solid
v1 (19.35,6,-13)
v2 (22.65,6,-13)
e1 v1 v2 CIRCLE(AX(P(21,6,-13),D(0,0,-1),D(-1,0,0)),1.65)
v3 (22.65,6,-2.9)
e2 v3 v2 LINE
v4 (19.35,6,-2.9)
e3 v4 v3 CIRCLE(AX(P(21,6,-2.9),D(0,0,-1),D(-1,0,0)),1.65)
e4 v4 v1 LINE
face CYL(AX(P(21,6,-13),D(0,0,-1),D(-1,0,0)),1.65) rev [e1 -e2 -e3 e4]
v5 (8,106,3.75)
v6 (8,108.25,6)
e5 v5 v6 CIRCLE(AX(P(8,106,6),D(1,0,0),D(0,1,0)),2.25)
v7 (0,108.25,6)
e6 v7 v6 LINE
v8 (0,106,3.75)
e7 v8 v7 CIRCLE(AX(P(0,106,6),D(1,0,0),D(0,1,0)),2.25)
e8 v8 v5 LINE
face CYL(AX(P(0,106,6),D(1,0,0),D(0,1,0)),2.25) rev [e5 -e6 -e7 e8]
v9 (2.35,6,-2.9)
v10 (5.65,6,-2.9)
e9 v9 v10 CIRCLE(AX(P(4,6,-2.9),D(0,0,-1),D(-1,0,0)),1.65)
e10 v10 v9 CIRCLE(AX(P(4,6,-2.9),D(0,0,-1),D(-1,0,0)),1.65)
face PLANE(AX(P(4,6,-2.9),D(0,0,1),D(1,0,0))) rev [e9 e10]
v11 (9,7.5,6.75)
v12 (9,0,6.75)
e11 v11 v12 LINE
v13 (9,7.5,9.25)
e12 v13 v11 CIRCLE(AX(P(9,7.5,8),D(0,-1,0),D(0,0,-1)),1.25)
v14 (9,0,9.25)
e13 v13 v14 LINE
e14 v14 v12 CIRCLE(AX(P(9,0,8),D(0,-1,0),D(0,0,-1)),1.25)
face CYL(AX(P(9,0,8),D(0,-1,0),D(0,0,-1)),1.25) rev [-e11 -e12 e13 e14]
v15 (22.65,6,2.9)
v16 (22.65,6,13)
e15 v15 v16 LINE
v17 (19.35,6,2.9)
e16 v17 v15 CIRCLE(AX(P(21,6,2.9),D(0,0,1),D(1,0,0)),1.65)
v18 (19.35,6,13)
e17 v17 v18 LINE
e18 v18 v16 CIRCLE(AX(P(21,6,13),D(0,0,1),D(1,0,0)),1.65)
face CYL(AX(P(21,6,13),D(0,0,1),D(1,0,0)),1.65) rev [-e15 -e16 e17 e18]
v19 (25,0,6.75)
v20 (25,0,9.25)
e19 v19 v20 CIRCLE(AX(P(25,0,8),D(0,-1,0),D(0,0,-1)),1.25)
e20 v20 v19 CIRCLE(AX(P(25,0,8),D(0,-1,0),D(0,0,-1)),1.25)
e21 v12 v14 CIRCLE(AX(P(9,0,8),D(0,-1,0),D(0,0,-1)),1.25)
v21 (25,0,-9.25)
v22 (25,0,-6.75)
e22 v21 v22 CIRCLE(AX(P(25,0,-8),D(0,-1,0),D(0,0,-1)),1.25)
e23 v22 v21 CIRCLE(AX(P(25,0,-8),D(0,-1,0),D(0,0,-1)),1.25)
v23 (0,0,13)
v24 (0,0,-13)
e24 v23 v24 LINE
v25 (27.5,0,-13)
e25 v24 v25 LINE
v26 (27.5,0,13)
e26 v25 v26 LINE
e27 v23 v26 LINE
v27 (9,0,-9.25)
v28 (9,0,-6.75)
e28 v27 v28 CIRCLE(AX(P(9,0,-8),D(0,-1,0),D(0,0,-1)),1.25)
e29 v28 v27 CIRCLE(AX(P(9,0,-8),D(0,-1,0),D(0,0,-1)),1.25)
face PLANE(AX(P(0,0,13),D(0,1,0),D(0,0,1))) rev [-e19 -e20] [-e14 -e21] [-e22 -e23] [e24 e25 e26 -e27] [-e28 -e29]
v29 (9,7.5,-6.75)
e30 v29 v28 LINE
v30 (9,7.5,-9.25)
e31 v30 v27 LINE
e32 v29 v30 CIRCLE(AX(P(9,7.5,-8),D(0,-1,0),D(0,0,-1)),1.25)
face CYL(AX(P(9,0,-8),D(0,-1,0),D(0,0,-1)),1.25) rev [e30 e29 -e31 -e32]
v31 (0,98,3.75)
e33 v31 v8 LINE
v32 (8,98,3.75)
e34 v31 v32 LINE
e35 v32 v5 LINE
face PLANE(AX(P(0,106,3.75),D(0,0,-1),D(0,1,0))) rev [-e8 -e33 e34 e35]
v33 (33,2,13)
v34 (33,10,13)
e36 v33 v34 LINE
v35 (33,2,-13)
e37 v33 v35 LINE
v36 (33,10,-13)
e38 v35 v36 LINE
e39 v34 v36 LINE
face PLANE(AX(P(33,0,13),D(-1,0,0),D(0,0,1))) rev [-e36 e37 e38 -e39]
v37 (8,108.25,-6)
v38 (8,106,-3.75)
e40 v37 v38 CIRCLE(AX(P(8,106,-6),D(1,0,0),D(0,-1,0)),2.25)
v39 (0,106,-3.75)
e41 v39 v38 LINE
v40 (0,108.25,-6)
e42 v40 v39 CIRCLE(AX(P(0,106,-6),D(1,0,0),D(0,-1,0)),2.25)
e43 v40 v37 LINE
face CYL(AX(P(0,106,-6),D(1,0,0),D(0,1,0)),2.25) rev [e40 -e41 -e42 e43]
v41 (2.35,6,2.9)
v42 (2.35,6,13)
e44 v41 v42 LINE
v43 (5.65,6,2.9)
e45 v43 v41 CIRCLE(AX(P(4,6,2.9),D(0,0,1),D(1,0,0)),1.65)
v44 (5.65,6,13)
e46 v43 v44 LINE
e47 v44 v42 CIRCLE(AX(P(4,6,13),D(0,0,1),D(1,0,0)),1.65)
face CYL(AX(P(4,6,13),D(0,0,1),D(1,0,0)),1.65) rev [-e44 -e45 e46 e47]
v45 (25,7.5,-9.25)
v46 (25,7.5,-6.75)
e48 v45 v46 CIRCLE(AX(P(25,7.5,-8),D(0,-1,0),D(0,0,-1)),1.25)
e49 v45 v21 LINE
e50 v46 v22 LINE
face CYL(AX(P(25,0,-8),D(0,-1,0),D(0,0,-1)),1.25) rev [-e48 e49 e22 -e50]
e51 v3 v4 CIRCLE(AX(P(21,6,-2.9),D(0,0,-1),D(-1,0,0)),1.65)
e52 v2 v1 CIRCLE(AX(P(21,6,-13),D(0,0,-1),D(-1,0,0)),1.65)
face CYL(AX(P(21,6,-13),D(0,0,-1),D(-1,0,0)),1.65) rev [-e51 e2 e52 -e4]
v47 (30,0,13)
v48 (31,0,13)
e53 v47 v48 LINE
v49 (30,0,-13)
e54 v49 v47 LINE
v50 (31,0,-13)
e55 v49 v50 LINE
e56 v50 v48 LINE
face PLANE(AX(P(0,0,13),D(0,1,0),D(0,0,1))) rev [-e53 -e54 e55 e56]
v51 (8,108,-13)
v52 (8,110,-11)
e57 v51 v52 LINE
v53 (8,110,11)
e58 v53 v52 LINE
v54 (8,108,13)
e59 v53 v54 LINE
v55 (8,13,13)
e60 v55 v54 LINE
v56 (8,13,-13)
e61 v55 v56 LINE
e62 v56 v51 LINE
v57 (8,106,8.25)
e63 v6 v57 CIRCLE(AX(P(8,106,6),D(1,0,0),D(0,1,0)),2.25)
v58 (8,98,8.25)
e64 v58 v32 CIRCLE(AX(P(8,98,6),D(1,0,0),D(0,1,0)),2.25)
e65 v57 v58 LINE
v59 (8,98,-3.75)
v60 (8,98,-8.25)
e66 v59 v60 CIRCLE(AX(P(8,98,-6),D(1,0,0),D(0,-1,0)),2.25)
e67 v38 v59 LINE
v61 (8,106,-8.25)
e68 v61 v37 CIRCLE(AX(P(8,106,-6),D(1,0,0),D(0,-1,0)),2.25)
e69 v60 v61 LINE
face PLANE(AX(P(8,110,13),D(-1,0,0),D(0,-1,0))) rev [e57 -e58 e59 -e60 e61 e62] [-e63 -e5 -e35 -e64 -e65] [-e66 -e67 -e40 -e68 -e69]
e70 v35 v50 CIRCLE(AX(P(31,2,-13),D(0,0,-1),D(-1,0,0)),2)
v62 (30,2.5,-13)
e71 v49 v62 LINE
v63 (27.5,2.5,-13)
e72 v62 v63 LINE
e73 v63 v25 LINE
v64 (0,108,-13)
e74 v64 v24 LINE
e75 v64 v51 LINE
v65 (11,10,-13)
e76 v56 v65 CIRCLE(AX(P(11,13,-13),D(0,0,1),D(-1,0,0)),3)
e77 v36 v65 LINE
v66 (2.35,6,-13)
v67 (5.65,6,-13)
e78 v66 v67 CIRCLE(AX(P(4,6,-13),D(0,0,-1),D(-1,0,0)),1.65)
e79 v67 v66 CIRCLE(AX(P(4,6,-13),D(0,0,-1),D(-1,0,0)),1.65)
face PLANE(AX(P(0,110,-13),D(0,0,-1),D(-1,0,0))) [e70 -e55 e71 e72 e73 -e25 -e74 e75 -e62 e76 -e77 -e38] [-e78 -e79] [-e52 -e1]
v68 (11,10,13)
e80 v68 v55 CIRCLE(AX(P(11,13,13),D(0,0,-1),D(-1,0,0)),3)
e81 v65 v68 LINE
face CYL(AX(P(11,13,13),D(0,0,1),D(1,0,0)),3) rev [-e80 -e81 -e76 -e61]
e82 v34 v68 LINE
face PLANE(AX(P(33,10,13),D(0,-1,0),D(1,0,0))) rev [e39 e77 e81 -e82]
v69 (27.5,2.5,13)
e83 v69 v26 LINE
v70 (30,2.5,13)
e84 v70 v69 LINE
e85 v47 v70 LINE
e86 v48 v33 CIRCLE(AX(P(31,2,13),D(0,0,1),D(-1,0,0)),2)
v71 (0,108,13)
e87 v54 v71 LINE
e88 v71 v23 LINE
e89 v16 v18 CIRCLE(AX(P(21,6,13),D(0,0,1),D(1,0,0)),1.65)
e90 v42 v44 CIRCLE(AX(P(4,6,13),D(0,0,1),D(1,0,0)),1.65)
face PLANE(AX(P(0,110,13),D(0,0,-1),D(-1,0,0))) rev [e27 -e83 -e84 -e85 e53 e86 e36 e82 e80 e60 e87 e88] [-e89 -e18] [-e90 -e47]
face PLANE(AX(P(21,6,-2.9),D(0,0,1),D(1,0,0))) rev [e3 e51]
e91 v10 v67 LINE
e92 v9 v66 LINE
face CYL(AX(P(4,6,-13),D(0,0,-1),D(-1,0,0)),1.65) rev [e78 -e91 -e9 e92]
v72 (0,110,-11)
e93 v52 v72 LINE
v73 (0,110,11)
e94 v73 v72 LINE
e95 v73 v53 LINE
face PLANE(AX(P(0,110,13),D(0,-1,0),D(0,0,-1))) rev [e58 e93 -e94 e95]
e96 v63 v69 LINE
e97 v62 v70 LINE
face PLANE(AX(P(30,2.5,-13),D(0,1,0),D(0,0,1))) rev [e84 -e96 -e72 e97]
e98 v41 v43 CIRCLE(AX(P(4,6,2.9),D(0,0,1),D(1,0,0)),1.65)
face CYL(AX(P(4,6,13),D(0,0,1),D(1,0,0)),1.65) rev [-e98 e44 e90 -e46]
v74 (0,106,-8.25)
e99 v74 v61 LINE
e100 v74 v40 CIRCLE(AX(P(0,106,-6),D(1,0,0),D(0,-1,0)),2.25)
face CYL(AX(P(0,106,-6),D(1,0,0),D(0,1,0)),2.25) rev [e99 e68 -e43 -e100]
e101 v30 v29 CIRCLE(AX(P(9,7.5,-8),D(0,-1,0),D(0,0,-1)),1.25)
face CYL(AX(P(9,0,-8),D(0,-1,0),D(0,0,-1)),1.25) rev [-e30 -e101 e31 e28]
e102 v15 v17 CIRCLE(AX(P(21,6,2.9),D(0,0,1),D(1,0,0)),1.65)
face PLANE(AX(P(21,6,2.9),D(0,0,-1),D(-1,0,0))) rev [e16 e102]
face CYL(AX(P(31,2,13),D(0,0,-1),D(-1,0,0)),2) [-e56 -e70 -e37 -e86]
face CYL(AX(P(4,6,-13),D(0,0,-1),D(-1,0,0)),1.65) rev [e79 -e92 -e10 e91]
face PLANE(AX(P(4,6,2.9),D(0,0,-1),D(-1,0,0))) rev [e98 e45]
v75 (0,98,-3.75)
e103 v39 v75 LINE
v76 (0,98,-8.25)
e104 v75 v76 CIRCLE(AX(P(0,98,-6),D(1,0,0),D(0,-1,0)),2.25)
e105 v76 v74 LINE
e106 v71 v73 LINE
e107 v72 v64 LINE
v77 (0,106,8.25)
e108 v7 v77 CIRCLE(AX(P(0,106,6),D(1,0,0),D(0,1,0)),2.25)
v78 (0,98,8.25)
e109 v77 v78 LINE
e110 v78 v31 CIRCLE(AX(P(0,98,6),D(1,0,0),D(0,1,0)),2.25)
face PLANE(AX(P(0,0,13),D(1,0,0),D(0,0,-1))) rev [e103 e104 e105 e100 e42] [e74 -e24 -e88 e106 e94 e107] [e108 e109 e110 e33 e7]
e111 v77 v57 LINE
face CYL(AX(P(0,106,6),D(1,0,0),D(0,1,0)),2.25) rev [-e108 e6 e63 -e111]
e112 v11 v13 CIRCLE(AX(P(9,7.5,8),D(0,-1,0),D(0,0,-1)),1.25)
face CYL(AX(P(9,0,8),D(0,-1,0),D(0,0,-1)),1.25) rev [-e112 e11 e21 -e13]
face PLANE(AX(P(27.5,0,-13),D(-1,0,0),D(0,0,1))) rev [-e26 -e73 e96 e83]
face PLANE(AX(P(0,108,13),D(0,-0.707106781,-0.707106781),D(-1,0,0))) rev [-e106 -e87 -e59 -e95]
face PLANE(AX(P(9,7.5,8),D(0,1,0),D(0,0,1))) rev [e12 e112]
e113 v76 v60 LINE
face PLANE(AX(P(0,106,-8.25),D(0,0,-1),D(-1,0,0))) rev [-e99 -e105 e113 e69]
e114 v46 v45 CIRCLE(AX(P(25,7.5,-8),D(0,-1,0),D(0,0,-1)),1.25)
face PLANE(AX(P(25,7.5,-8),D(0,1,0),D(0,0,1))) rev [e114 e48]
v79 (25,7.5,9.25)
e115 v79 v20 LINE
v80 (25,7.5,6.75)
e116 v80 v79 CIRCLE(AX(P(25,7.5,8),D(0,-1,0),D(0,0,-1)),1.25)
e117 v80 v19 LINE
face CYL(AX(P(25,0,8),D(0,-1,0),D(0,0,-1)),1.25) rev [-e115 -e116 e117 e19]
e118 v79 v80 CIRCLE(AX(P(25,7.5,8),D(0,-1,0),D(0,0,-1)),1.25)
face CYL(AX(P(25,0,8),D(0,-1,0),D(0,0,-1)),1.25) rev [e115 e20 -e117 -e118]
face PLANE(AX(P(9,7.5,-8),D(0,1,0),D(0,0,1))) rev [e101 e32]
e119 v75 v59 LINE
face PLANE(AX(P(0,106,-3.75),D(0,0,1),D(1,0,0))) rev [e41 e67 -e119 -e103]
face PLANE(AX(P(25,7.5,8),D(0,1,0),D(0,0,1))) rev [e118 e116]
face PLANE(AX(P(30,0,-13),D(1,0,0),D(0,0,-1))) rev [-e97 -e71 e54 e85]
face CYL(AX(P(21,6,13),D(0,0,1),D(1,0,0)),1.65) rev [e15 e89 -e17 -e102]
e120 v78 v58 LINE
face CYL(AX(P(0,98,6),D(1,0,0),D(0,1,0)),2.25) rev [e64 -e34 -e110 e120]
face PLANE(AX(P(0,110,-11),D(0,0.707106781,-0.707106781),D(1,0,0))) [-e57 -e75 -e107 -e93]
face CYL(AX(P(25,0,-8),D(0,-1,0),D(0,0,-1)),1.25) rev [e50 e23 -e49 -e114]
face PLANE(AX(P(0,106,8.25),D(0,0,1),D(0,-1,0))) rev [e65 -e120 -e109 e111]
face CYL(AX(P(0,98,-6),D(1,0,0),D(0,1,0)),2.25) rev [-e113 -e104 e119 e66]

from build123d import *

# Parameters (mm, degrees)
BOSS_EXTRUDE1_DEPTH   = 13
SKETCH2_W             = 2.5
SKETCH2_H             = 2.5
CUT_EXTRUDE1_DEPTH    = 118.749734607
M4_TAPPED_HOLE1_D     = 3.3
M4_TAPPED_HOLE1_DEPTH = 10.1
M3_TAPPED_HOLE1_D     = 2.5
M3_TAPPED_HOLE1_DEPTH = 7.5
CUT_EXTRUDE2_DEPTH    = 114.551750317
FILLET1_R             = 2
FILLET2_R             = 3
CHAMFER1_SIZE         = 2


with BuildPart() as part:
    # Sketch1 → Boss-Extrude1 (new, symmetric)
    with BuildSketch(Plane.XY):
        Polygon((0, 110), (8, 110), (8, 10), (33, 10), (33, 0), (0, 0), align=None)
    extrude(amount=BOSS_EXTRUDE1_DEPTH, both=True)

    # Sketch2 → Cut-Extrude1 (cut, through all)
    with BuildSketch(Plane.XY.offset(13)):
        with Locations((28.75, 1.25)):
            Rectangle(SKETCH2_W, SKETCH2_H)
    extrude(amount=-CUT_EXTRUDE1_DEPTH, mode=Mode.SUBTRACT)

    # M4 Tapped Hole1
    with Locations(Plane.XY.offset(13)):
        with Locations((21, 6), (4, 6)):
            m4_tapped_hole1 = Hole(M4_TAPPED_HOLE1_D / 2, depth=M4_TAPPED_HOLE1_DEPTH)

    # Mirror1: M4 Tapped Hole1 across plane
    add(m4_tapped_hole1.mirror(Plane.XY), mode=Mode.SUBTRACT)

    # M3 Tapped Hole1
    with Locations(Plane.XZ):
        with Locations((25, 8), (9, 8), (9, -8), (25, -8)):
            Hole(M3_TAPPED_HOLE1_D / 2, depth=M3_TAPPED_HOLE1_DEPTH)

    # Sketch7 → Cut-Extrude2 (cut, through all)
    with BuildSketch(Plane(origin=(8, 0, 0), x_dir=(0, 0, -1), z_dir=(1, 0, 0))):
        with BuildLine():
            Line((-3.75, 106), (-3.75, 98))
            ThreePointArc((-3.75, 98), (-6, 95.75), (-8.25, 98))
            Line((-8.25, 98), (-8.25, 106))
            ThreePointArc((-8.25, 106), (-6, 108.25), (-3.75, 106))
        make_face()
        with BuildLine():
            Line((3.75, 106), (3.75, 98))
            ThreePointArc((3.75, 98), (6, 95.75), (8.25, 98))
            Line((8.25, 98), (8.25, 106))
            ThreePointArc((8.25, 106), (6, 108.25), (3.75, 106))
        make_face()
    extrude(amount=-CUT_EXTRUDE2_DEPTH, mode=Mode.SUBTRACT)

    # Fillet1
    fillet1_edges = [part.edges().sort_by_distance(p)[0] for p in [
        (33, 0, 0),
    ]]
    fillet(fillet1_edges, radius=FILLET1_R)

    # Fillet2
    fillet2_edges = [part.edges().sort_by_distance(p)[0] for p in [
        (8, 10, 0),
    ]]
    fillet(fillet2_edges, radius=FILLET2_R)

    # Chamfer1
    chamfer1_edges = [part.edges().sort_by_distance(p)[0] for p in [
        (4, 110, 13),
        (4, 110, -13),
    ]]
    chamfer(chamfer1_edges, length=CHAMFER1_SIZE)


solid = part.part
